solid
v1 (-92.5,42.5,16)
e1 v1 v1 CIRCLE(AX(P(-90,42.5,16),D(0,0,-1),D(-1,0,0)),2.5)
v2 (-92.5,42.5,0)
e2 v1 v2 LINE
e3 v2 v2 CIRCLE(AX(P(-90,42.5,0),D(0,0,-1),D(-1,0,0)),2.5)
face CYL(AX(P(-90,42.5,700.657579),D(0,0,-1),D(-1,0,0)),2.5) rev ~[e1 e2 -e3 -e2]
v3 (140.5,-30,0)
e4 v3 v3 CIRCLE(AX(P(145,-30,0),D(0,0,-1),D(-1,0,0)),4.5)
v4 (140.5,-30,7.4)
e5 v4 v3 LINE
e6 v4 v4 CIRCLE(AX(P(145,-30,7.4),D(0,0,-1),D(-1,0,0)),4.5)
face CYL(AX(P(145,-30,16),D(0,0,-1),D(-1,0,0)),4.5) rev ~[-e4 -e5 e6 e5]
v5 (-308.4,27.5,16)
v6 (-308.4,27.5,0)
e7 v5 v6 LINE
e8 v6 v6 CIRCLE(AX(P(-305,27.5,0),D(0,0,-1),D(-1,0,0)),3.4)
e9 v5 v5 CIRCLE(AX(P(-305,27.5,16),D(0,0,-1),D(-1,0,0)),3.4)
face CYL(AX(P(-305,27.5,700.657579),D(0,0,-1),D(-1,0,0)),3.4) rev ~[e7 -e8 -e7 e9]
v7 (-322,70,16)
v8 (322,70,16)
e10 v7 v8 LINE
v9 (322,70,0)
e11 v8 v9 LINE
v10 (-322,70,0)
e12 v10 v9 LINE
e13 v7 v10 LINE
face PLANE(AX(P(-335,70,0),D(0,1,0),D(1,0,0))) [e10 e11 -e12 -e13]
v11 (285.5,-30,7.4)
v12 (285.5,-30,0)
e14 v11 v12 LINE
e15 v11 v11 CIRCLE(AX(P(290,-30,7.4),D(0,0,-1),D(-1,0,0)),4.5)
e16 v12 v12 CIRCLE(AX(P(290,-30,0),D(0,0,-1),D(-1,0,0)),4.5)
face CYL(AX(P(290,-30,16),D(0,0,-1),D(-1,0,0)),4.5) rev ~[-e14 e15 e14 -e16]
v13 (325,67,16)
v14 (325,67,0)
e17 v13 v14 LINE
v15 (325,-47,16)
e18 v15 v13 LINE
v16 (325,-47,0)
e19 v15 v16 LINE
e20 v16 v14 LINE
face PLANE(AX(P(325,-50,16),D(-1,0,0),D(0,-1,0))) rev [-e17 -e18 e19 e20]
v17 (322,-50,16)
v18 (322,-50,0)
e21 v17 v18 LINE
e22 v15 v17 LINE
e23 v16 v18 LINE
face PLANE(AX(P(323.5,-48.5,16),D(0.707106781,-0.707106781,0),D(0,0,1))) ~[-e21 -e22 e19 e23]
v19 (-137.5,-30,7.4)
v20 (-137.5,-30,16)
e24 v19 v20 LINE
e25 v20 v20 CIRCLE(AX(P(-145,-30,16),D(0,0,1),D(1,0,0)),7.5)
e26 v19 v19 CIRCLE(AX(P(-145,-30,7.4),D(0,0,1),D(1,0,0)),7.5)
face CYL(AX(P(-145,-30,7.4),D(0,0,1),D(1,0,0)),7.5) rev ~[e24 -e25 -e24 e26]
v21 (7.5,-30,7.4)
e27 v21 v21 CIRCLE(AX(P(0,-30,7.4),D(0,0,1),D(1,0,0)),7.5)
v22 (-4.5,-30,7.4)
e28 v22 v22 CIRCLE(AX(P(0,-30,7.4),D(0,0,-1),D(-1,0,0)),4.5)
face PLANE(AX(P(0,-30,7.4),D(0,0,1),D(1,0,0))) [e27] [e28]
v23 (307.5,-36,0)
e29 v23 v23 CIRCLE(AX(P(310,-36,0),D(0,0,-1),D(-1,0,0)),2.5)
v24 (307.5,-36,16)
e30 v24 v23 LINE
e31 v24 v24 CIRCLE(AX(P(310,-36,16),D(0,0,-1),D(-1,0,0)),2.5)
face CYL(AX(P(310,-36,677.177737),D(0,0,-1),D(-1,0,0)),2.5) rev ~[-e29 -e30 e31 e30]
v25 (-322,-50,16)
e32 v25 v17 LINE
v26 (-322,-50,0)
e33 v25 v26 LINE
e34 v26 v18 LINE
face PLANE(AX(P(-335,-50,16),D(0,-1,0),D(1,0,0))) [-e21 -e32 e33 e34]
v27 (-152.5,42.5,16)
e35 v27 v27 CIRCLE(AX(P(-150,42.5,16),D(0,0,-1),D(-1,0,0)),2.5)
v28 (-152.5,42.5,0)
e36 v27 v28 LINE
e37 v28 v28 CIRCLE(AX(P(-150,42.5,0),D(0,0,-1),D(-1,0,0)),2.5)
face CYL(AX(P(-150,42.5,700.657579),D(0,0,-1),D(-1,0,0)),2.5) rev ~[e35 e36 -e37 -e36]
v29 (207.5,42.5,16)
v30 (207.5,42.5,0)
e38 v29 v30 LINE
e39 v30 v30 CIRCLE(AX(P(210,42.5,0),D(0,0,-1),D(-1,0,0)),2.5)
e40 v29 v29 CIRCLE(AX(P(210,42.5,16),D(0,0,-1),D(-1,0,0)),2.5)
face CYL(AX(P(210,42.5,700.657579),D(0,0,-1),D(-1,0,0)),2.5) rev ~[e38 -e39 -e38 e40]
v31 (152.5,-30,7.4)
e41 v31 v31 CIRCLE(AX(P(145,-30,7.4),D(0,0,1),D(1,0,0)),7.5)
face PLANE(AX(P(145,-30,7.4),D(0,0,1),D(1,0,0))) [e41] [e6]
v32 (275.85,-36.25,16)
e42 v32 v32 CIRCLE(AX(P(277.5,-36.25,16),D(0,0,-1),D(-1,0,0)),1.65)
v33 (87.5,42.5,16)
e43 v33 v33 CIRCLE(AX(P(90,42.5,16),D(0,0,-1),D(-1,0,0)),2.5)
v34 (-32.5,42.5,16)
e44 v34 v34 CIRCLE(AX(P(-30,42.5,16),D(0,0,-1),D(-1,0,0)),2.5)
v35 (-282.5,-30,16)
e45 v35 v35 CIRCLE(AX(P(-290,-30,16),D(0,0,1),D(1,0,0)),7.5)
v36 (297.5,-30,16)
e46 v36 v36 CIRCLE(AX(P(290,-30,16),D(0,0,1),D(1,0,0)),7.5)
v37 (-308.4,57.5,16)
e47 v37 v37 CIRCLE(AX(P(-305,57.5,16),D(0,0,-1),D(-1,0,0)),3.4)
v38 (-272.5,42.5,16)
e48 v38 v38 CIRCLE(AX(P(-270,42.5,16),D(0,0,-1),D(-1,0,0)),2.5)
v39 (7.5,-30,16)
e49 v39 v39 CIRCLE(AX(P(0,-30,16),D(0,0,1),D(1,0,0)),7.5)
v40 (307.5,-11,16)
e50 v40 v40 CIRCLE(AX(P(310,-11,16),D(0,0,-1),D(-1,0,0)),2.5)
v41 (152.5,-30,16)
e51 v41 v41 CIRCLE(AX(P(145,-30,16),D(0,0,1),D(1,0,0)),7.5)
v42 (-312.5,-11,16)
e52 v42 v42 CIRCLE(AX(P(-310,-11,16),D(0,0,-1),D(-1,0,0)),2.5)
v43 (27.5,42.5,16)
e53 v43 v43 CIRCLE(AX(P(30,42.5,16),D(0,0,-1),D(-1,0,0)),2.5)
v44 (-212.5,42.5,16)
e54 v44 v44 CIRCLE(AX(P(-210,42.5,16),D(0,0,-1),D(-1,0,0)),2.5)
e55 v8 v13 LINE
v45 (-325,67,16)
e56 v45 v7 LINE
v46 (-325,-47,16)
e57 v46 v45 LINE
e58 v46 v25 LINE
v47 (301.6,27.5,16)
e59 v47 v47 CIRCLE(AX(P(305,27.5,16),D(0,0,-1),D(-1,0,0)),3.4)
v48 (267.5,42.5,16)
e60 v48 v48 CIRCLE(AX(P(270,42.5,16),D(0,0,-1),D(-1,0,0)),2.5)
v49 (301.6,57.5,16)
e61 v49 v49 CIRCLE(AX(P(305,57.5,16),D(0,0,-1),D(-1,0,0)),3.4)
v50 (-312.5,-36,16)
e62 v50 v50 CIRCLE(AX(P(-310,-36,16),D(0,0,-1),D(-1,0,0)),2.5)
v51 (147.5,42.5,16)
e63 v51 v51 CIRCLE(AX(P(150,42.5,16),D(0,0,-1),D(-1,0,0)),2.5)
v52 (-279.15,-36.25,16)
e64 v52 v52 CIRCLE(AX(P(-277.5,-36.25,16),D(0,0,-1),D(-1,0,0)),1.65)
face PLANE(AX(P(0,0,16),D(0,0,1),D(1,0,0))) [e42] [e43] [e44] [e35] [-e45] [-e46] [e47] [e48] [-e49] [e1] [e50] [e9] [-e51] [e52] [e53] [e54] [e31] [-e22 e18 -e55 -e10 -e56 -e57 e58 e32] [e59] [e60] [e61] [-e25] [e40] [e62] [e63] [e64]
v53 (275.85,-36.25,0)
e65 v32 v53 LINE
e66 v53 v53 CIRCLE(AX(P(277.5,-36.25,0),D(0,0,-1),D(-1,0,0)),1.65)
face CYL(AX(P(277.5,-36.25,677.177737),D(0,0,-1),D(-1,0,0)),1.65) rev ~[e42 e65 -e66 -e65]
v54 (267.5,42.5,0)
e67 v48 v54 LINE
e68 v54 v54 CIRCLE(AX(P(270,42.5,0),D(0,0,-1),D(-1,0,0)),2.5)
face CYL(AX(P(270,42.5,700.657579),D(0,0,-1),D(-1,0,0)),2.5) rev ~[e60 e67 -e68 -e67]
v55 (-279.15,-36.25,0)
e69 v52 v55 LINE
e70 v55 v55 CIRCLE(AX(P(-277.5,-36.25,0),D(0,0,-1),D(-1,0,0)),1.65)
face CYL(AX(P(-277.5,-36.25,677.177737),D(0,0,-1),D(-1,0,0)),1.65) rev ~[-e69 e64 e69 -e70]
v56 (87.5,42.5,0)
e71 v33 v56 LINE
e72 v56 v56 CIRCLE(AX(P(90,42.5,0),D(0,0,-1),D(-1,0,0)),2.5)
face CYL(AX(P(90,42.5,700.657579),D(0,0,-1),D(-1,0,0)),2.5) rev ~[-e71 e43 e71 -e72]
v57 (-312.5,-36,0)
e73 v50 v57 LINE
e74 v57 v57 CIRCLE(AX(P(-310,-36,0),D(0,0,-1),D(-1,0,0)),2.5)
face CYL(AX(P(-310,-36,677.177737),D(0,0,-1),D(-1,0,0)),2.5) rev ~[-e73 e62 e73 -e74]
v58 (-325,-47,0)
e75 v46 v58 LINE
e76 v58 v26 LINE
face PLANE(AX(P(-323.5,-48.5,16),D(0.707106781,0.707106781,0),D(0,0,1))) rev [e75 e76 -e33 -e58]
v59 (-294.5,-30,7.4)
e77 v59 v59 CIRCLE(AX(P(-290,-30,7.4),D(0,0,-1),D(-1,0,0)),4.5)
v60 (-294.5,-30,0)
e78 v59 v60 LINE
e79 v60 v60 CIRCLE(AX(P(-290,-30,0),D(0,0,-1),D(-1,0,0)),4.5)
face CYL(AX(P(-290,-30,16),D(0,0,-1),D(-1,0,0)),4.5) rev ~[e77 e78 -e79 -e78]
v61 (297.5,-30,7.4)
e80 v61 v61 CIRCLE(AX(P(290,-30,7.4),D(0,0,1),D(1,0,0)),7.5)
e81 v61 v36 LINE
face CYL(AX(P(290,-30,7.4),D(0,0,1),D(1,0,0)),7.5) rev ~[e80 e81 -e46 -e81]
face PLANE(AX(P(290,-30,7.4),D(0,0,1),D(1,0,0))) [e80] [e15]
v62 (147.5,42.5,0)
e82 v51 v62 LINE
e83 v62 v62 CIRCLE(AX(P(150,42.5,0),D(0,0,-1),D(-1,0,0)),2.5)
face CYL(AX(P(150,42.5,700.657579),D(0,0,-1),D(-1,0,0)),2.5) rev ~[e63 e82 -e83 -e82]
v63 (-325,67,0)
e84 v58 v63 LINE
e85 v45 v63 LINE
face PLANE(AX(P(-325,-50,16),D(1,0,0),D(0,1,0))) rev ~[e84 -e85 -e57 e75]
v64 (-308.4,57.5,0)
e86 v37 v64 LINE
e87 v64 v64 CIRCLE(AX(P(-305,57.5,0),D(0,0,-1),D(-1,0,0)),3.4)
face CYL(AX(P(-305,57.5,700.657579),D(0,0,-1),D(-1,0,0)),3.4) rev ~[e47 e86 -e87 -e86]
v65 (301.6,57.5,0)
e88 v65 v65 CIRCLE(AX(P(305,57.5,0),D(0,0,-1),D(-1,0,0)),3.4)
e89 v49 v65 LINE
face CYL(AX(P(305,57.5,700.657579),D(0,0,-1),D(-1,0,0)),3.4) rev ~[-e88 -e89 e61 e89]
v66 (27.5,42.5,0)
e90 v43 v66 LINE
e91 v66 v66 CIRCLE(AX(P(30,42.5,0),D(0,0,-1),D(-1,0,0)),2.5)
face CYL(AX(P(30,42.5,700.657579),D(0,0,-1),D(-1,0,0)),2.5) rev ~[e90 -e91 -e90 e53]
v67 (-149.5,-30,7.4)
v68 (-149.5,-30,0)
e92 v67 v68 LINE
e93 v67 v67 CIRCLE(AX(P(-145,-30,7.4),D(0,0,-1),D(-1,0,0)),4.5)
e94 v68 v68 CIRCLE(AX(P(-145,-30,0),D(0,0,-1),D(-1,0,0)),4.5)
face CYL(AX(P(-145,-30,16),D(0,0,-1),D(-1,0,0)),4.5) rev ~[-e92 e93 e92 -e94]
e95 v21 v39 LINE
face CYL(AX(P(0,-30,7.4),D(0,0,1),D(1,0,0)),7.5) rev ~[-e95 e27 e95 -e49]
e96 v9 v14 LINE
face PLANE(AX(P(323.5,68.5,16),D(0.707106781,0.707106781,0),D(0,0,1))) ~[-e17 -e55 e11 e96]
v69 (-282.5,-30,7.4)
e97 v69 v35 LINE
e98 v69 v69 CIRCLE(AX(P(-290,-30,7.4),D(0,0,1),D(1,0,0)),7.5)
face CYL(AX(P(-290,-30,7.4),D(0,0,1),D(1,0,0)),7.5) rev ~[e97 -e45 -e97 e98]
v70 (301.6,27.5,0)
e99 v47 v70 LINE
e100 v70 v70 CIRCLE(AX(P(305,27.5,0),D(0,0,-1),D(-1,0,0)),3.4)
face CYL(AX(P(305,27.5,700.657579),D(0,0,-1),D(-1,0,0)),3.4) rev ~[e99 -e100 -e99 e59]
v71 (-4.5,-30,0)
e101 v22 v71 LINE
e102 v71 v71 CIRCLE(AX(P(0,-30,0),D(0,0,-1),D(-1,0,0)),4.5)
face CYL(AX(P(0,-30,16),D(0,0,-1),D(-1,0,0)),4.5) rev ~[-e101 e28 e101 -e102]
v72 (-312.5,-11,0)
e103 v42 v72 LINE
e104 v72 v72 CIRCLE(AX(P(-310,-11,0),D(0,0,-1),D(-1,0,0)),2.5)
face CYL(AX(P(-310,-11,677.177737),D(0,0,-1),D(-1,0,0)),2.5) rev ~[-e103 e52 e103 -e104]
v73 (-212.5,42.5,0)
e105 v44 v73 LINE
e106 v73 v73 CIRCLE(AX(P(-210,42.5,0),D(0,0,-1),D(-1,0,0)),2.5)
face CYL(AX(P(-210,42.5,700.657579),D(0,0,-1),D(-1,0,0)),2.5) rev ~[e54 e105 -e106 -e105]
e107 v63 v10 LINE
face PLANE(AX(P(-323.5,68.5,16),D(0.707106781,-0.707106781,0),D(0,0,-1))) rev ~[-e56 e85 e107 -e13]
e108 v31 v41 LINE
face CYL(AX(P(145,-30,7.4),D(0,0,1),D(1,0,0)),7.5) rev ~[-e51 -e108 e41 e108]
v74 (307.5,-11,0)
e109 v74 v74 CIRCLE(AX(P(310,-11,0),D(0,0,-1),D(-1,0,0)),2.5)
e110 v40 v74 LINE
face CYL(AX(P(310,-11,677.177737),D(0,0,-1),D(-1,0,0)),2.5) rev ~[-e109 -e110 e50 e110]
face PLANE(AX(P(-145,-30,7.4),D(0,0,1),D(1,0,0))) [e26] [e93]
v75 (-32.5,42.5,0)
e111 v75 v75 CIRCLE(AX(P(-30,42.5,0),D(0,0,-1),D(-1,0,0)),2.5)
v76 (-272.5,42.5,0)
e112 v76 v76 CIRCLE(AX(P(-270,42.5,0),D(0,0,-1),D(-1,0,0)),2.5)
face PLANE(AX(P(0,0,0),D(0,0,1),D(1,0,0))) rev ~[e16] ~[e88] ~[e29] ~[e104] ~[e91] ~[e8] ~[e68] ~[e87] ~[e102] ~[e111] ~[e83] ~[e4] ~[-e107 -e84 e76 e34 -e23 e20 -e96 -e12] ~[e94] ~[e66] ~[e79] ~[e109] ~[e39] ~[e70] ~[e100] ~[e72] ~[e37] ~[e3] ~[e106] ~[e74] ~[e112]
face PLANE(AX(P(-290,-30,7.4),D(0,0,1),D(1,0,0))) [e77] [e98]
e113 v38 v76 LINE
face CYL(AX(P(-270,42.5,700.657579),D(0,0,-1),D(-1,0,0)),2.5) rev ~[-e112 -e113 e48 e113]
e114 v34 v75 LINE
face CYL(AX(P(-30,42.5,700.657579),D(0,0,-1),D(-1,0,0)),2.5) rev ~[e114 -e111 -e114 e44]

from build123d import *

# Parameters (mm, degrees)
SKETCH_1_W                     = 670
SKETCH_1_H                     = 140
EXTRUDE_1_DEPTH                = 16
HOLE_WIZARD_M8_1_D             = 6.8
HOLE_WIZARD_M6_1_D             = 5
HOLE_WIZARD_M8_1_2_D           = 9
HOLE_WIZARD_M8_1_2_CBORE_D     = 15
HOLE_WIZARD_M8_1_2_CBORE_DEPTH = 8.6
SKETCH_16_W                    = 670
SKETCH_16_H                    = 20
CUT_EXTRUDE_1_DEPTH            = 343.609106709
SKETCH_19_W                    = 10
SKETCH_19_H                    = 120
CUT_EXTRUDE_2_DEPTH            = 343.609106709
CHAMFER_1_SIZE                 = 3
HOLE_WIZARD_M6_2_D             = 5
HOLE_WIZARD_M4_1_D             = 3.3


with BuildPart() as part:
    # 草图1 → 凸台-拉伸1 (new body)
    with BuildSketch(Plane.XY):
        Rectangle(SKETCH_1_W, SKETCH_1_H)
    extrude(amount=EXTRUDE_1_DEPTH)

    # Hole Wizard M8 _1 (through all)
    with Locations(Plane.XY.offset(16)):
        with Locations((-305, 57.5), (-305, 27.5), (305, 27.5), (305, 57.5)):
            Hole(HOLE_WIZARD_M8_1_D / 2)

    # M6 螺纹孔1 (through all)
    with Locations(Plane.XY.offset(16)):
        with Locations((-270, 42.5), (-210, 42.5), (-150, 42.5), (-90, 42.5), (-30, 42.5), (30, 42.5), (90, 42.5), (150, 42.5), (210, 42.5), (270, 42.5)):
            Hole(HOLE_WIZARD_M6_1_D / 2)

    # Hole Wizard M8 _1 2 (through all)
    with Locations(Plane.XY.offset(16)):
        with Locations((290, -30), (145, -30), (0, -30), (-145, -30), (-290, -30), (-435, -30)):
            CounterBoreHole(HOLE_WIZARD_M8_1_2_D / 2, HOLE_WIZARD_M8_1_2_CBORE_D / 2, HOLE_WIZARD_M8_1_2_CBORE_DEPTH)

    # 草图16 → 切除-拉伸1 (cut, through all)
    with BuildSketch(Plane.XY.offset(16)):
        with Locations((0, -60)):
            Rectangle(SKETCH_16_W, SKETCH_16_H)
    extrude(amount=-CUT_EXTRUDE_1_DEPTH, mode=Mode.SUBTRACT)

    # 草图19 → 切除-拉伸2 (cut, through all)
    with BuildSketch(Plane.XY.offset(16)):
        with Locations((-330, 10)):
            Rectangle(SKETCH_19_W, SKETCH_19_H)
    cut_extrude_2 = extrude(amount=-CUT_EXTRUDE_2_DEPTH, mode=Mode.SUBTRACT)

    # 镜向1: 切除-拉伸2 across plane
    add(cut_extrude_2.mirror(Plane(origin=(0, 0, 0), x_dir=(0, 0, 1), z_dir=(1, 0, 0))), mode=Mode.SUBTRACT)

    # 倒角1
    chamfer_1_edges = [part.edges().sort_by_distance(p)[0] for p in [
        (-325, 70, 8),
        (-325, -50, 8),
        (325, -50, 8),
        (325, 70, 8),
    ]]
    chamfer(chamfer_1_edges, length=CHAMFER_1_SIZE)

    # M6 螺纹孔2 (through all)
    with Locations(Plane.XY.offset(16)):
        with Locations((-310, -11), (-310, -36), (310, -11), (310, -36)):
            Hole(HOLE_WIZARD_M6_2_D / 2)

    # M4 螺纹孔1 (through all)
    with Locations(Plane.XY.offset(16)):
        with Locations((277.5, -36.25), (-277.5, -36.25)):
            Hole(HOLE_WIZARD_M4_1_D / 2)


solid = part.part
